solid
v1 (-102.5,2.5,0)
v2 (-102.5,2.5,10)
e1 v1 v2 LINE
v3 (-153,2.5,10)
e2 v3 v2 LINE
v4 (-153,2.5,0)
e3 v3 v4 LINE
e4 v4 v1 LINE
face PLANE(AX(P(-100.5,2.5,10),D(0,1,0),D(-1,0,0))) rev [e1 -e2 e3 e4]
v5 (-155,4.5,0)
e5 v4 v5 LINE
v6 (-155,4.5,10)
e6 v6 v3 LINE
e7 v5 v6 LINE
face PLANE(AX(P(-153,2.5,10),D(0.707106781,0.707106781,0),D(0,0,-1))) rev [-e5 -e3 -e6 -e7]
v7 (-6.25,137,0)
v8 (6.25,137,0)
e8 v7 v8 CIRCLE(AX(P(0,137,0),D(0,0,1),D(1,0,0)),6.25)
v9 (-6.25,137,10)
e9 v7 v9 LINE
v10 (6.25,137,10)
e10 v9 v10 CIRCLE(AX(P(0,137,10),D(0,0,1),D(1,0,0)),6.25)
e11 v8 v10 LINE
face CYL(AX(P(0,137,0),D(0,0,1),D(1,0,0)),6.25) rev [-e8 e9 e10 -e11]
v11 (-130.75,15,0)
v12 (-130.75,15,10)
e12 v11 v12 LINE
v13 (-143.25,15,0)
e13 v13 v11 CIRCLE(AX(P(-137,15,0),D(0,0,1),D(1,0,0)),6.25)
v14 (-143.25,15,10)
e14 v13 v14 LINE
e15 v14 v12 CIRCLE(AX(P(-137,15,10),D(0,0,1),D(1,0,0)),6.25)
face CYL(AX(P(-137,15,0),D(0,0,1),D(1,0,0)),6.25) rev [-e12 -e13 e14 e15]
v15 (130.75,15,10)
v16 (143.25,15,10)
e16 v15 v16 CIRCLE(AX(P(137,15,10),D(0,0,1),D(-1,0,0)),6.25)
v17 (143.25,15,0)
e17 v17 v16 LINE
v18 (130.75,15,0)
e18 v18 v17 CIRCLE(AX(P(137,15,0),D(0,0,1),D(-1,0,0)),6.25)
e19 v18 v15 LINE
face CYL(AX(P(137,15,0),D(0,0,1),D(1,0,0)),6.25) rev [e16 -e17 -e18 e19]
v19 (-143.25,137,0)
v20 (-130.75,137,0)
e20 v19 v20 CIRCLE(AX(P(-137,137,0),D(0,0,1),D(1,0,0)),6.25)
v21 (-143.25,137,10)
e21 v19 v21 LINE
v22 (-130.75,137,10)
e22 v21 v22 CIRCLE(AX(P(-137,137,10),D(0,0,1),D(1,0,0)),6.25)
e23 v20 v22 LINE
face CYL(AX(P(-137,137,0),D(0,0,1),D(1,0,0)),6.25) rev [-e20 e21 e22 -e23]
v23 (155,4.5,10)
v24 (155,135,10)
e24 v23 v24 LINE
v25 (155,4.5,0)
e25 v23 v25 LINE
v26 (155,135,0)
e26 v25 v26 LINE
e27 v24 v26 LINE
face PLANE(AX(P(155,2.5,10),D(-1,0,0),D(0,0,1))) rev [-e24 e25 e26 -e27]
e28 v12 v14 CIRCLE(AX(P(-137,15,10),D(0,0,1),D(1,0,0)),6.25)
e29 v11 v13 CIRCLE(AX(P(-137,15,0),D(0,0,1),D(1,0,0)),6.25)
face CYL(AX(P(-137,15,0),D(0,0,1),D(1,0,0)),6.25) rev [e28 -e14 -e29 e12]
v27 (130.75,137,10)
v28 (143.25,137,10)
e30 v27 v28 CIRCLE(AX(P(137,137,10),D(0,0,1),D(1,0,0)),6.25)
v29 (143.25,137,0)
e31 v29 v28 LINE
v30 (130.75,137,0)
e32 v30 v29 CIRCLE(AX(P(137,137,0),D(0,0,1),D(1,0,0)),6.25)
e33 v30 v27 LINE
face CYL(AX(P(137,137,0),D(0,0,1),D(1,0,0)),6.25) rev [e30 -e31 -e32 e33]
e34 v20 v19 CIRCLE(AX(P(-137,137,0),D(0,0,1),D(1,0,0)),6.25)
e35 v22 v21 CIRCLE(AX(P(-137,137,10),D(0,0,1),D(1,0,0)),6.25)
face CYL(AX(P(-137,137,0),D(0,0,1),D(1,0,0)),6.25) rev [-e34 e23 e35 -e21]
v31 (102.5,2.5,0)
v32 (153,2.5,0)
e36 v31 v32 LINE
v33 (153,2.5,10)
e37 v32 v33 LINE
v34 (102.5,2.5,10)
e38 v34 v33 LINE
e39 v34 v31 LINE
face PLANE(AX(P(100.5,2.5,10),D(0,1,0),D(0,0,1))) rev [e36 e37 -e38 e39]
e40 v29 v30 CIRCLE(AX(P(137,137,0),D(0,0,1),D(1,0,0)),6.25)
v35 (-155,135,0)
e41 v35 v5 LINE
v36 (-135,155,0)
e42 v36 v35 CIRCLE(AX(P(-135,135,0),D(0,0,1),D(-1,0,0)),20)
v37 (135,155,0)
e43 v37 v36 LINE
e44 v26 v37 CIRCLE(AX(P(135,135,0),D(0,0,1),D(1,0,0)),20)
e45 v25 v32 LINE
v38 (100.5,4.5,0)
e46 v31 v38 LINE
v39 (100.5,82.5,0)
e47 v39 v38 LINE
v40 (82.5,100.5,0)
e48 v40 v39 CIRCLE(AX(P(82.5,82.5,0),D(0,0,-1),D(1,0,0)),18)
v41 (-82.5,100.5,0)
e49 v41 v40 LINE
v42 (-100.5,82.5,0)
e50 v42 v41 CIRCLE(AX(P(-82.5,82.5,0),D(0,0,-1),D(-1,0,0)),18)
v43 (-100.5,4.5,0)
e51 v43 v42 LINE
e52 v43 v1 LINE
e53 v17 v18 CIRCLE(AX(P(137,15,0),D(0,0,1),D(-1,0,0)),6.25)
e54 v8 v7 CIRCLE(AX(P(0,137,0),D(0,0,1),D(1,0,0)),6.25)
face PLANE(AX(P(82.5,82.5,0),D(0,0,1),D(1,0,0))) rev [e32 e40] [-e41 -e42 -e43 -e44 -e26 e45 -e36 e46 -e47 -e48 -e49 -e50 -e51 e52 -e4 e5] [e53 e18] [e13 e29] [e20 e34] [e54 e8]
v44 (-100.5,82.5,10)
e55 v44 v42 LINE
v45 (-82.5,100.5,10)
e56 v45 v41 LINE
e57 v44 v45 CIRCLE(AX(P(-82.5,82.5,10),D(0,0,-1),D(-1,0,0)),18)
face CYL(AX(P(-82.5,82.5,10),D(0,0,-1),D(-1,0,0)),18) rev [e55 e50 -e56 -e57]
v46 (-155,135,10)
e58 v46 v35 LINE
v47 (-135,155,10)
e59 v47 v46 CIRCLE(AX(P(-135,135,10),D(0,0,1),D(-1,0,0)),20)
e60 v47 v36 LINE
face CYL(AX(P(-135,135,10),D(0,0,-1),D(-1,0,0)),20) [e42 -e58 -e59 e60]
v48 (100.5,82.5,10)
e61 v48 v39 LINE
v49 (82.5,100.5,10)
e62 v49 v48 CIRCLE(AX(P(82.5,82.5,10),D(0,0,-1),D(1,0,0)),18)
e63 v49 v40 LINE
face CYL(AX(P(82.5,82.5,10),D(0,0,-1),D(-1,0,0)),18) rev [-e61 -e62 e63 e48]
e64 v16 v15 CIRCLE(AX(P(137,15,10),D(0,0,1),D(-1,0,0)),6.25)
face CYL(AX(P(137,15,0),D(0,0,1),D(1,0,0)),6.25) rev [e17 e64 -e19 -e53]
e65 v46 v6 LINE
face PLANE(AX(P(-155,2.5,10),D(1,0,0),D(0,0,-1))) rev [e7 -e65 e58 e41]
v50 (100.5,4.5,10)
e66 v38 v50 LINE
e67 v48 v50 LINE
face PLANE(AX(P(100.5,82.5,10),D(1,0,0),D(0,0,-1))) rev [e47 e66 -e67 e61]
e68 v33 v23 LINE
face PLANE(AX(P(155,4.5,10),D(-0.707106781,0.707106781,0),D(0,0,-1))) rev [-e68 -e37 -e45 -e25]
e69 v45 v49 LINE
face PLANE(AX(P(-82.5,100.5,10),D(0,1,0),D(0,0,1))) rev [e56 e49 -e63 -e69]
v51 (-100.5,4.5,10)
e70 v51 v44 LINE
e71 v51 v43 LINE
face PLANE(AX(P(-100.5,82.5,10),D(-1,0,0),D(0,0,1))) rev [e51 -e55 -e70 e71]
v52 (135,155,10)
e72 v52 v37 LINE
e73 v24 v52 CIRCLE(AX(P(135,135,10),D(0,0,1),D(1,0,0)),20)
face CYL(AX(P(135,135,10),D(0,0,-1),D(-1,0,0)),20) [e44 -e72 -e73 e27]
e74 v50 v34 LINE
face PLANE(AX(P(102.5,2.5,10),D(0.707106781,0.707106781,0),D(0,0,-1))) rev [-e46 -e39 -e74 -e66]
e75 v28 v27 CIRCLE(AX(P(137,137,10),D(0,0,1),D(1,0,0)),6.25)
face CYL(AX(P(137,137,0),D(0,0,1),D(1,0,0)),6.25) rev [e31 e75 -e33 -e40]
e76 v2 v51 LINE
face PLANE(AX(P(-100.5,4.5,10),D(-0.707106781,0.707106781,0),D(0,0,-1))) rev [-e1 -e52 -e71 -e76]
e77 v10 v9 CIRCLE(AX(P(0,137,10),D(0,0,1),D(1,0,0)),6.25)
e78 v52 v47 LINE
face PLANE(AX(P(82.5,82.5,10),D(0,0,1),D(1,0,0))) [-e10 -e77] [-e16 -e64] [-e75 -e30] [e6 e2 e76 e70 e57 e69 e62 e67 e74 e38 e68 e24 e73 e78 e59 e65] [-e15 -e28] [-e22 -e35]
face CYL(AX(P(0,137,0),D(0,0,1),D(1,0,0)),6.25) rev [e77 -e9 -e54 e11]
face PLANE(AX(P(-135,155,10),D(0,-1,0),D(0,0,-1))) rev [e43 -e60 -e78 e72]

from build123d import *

# Parameters (mm, degrees)
EXTRUDE_1_DEPTH     = 10
SKETCH_2_R          = 6.25
CUT_EXTRUDE_1_DEPTH = 220.431082575
CHAMFER_1_SIZE      = 2


with BuildPart() as part:
    # 草图1 → 凸台-拉伸1 (new body)
    with BuildSketch(Plane.XY):
        with BuildLine():
            Line((-82.5, 100.5), (82.5, 100.5))
            ThreePointArc((82.5, 100.5), (95.227922061, 95.227922061), (100.5, 82.5))
            Line((100.5, 82.5), (100.5, 2.5))
            Line((100.5, 2.5), (155, 2.5))
            Line((155, 2.5), (155, 135))
            ThreePointArc((155, 135), (149.142135624, 149.142135624), (135, 155))
            Line((135, 155), (-135, 155))
            ThreePointArc((-135, 155), (-149.142135624, 149.142135624), (-155, 135))
            Line((-155, 135), (-155, 2.5))
            Line((-155, 2.5), (-100.5, 2.5))
            Line((-100.5, 2.5), (-100.5, 82.5))
            ThreePointArc((-100.5, 82.5), (-95.227922061, 95.227922061), (-82.5, 100.5))
        make_face()
    extrude(amount=EXTRUDE_1_DEPTH)

    # 草图2 → 切除-拉伸1 (cut, through all)
    with BuildSketch(Plane.XY.offset(10)):
        with Locations((0, 137)):
            Circle(SKETCH_2_R)
        with Locations((0, -137)):
            Circle(SKETCH_2_R)
        with Locations((-137, 137)):
            Circle(SKETCH_2_R)
        with Locations((137, 137)):
            Circle(SKETCH_2_R)
        with Locations((-137, -137)):
            Circle(SKETCH_2_R)
        with Locations((137, -137)):
            Circle(SKETCH_2_R)
        with Locations((-137, 15)):
            Circle(SKETCH_2_R)
        with Locations((-137, -15)):
            Circle(SKETCH_2_R)
        with Locations((137, -15)):
            Circle(SKETCH_2_R)
        with Locations(Location((137, 15, 0), (0, 0, 180))):
            Circle(SKETCH_2_R)
    extrude(amount=-CUT_EXTRUDE_1_DEPTH, mode=Mode.SUBTRACT)

    # 倒角1
    chamfer_1_edges = [part.edges().sort_by_distance(p)[0] for p in [
        (-100.5, 2.5, 5),
        (-155, 2.5, 5),
        (155, 2.5, 5),
        (100.5, 2.5, 5),
    ]]
    chamfer(chamfer_1_edges, length=CHAMFER_1_SIZE)


solid = part.part
